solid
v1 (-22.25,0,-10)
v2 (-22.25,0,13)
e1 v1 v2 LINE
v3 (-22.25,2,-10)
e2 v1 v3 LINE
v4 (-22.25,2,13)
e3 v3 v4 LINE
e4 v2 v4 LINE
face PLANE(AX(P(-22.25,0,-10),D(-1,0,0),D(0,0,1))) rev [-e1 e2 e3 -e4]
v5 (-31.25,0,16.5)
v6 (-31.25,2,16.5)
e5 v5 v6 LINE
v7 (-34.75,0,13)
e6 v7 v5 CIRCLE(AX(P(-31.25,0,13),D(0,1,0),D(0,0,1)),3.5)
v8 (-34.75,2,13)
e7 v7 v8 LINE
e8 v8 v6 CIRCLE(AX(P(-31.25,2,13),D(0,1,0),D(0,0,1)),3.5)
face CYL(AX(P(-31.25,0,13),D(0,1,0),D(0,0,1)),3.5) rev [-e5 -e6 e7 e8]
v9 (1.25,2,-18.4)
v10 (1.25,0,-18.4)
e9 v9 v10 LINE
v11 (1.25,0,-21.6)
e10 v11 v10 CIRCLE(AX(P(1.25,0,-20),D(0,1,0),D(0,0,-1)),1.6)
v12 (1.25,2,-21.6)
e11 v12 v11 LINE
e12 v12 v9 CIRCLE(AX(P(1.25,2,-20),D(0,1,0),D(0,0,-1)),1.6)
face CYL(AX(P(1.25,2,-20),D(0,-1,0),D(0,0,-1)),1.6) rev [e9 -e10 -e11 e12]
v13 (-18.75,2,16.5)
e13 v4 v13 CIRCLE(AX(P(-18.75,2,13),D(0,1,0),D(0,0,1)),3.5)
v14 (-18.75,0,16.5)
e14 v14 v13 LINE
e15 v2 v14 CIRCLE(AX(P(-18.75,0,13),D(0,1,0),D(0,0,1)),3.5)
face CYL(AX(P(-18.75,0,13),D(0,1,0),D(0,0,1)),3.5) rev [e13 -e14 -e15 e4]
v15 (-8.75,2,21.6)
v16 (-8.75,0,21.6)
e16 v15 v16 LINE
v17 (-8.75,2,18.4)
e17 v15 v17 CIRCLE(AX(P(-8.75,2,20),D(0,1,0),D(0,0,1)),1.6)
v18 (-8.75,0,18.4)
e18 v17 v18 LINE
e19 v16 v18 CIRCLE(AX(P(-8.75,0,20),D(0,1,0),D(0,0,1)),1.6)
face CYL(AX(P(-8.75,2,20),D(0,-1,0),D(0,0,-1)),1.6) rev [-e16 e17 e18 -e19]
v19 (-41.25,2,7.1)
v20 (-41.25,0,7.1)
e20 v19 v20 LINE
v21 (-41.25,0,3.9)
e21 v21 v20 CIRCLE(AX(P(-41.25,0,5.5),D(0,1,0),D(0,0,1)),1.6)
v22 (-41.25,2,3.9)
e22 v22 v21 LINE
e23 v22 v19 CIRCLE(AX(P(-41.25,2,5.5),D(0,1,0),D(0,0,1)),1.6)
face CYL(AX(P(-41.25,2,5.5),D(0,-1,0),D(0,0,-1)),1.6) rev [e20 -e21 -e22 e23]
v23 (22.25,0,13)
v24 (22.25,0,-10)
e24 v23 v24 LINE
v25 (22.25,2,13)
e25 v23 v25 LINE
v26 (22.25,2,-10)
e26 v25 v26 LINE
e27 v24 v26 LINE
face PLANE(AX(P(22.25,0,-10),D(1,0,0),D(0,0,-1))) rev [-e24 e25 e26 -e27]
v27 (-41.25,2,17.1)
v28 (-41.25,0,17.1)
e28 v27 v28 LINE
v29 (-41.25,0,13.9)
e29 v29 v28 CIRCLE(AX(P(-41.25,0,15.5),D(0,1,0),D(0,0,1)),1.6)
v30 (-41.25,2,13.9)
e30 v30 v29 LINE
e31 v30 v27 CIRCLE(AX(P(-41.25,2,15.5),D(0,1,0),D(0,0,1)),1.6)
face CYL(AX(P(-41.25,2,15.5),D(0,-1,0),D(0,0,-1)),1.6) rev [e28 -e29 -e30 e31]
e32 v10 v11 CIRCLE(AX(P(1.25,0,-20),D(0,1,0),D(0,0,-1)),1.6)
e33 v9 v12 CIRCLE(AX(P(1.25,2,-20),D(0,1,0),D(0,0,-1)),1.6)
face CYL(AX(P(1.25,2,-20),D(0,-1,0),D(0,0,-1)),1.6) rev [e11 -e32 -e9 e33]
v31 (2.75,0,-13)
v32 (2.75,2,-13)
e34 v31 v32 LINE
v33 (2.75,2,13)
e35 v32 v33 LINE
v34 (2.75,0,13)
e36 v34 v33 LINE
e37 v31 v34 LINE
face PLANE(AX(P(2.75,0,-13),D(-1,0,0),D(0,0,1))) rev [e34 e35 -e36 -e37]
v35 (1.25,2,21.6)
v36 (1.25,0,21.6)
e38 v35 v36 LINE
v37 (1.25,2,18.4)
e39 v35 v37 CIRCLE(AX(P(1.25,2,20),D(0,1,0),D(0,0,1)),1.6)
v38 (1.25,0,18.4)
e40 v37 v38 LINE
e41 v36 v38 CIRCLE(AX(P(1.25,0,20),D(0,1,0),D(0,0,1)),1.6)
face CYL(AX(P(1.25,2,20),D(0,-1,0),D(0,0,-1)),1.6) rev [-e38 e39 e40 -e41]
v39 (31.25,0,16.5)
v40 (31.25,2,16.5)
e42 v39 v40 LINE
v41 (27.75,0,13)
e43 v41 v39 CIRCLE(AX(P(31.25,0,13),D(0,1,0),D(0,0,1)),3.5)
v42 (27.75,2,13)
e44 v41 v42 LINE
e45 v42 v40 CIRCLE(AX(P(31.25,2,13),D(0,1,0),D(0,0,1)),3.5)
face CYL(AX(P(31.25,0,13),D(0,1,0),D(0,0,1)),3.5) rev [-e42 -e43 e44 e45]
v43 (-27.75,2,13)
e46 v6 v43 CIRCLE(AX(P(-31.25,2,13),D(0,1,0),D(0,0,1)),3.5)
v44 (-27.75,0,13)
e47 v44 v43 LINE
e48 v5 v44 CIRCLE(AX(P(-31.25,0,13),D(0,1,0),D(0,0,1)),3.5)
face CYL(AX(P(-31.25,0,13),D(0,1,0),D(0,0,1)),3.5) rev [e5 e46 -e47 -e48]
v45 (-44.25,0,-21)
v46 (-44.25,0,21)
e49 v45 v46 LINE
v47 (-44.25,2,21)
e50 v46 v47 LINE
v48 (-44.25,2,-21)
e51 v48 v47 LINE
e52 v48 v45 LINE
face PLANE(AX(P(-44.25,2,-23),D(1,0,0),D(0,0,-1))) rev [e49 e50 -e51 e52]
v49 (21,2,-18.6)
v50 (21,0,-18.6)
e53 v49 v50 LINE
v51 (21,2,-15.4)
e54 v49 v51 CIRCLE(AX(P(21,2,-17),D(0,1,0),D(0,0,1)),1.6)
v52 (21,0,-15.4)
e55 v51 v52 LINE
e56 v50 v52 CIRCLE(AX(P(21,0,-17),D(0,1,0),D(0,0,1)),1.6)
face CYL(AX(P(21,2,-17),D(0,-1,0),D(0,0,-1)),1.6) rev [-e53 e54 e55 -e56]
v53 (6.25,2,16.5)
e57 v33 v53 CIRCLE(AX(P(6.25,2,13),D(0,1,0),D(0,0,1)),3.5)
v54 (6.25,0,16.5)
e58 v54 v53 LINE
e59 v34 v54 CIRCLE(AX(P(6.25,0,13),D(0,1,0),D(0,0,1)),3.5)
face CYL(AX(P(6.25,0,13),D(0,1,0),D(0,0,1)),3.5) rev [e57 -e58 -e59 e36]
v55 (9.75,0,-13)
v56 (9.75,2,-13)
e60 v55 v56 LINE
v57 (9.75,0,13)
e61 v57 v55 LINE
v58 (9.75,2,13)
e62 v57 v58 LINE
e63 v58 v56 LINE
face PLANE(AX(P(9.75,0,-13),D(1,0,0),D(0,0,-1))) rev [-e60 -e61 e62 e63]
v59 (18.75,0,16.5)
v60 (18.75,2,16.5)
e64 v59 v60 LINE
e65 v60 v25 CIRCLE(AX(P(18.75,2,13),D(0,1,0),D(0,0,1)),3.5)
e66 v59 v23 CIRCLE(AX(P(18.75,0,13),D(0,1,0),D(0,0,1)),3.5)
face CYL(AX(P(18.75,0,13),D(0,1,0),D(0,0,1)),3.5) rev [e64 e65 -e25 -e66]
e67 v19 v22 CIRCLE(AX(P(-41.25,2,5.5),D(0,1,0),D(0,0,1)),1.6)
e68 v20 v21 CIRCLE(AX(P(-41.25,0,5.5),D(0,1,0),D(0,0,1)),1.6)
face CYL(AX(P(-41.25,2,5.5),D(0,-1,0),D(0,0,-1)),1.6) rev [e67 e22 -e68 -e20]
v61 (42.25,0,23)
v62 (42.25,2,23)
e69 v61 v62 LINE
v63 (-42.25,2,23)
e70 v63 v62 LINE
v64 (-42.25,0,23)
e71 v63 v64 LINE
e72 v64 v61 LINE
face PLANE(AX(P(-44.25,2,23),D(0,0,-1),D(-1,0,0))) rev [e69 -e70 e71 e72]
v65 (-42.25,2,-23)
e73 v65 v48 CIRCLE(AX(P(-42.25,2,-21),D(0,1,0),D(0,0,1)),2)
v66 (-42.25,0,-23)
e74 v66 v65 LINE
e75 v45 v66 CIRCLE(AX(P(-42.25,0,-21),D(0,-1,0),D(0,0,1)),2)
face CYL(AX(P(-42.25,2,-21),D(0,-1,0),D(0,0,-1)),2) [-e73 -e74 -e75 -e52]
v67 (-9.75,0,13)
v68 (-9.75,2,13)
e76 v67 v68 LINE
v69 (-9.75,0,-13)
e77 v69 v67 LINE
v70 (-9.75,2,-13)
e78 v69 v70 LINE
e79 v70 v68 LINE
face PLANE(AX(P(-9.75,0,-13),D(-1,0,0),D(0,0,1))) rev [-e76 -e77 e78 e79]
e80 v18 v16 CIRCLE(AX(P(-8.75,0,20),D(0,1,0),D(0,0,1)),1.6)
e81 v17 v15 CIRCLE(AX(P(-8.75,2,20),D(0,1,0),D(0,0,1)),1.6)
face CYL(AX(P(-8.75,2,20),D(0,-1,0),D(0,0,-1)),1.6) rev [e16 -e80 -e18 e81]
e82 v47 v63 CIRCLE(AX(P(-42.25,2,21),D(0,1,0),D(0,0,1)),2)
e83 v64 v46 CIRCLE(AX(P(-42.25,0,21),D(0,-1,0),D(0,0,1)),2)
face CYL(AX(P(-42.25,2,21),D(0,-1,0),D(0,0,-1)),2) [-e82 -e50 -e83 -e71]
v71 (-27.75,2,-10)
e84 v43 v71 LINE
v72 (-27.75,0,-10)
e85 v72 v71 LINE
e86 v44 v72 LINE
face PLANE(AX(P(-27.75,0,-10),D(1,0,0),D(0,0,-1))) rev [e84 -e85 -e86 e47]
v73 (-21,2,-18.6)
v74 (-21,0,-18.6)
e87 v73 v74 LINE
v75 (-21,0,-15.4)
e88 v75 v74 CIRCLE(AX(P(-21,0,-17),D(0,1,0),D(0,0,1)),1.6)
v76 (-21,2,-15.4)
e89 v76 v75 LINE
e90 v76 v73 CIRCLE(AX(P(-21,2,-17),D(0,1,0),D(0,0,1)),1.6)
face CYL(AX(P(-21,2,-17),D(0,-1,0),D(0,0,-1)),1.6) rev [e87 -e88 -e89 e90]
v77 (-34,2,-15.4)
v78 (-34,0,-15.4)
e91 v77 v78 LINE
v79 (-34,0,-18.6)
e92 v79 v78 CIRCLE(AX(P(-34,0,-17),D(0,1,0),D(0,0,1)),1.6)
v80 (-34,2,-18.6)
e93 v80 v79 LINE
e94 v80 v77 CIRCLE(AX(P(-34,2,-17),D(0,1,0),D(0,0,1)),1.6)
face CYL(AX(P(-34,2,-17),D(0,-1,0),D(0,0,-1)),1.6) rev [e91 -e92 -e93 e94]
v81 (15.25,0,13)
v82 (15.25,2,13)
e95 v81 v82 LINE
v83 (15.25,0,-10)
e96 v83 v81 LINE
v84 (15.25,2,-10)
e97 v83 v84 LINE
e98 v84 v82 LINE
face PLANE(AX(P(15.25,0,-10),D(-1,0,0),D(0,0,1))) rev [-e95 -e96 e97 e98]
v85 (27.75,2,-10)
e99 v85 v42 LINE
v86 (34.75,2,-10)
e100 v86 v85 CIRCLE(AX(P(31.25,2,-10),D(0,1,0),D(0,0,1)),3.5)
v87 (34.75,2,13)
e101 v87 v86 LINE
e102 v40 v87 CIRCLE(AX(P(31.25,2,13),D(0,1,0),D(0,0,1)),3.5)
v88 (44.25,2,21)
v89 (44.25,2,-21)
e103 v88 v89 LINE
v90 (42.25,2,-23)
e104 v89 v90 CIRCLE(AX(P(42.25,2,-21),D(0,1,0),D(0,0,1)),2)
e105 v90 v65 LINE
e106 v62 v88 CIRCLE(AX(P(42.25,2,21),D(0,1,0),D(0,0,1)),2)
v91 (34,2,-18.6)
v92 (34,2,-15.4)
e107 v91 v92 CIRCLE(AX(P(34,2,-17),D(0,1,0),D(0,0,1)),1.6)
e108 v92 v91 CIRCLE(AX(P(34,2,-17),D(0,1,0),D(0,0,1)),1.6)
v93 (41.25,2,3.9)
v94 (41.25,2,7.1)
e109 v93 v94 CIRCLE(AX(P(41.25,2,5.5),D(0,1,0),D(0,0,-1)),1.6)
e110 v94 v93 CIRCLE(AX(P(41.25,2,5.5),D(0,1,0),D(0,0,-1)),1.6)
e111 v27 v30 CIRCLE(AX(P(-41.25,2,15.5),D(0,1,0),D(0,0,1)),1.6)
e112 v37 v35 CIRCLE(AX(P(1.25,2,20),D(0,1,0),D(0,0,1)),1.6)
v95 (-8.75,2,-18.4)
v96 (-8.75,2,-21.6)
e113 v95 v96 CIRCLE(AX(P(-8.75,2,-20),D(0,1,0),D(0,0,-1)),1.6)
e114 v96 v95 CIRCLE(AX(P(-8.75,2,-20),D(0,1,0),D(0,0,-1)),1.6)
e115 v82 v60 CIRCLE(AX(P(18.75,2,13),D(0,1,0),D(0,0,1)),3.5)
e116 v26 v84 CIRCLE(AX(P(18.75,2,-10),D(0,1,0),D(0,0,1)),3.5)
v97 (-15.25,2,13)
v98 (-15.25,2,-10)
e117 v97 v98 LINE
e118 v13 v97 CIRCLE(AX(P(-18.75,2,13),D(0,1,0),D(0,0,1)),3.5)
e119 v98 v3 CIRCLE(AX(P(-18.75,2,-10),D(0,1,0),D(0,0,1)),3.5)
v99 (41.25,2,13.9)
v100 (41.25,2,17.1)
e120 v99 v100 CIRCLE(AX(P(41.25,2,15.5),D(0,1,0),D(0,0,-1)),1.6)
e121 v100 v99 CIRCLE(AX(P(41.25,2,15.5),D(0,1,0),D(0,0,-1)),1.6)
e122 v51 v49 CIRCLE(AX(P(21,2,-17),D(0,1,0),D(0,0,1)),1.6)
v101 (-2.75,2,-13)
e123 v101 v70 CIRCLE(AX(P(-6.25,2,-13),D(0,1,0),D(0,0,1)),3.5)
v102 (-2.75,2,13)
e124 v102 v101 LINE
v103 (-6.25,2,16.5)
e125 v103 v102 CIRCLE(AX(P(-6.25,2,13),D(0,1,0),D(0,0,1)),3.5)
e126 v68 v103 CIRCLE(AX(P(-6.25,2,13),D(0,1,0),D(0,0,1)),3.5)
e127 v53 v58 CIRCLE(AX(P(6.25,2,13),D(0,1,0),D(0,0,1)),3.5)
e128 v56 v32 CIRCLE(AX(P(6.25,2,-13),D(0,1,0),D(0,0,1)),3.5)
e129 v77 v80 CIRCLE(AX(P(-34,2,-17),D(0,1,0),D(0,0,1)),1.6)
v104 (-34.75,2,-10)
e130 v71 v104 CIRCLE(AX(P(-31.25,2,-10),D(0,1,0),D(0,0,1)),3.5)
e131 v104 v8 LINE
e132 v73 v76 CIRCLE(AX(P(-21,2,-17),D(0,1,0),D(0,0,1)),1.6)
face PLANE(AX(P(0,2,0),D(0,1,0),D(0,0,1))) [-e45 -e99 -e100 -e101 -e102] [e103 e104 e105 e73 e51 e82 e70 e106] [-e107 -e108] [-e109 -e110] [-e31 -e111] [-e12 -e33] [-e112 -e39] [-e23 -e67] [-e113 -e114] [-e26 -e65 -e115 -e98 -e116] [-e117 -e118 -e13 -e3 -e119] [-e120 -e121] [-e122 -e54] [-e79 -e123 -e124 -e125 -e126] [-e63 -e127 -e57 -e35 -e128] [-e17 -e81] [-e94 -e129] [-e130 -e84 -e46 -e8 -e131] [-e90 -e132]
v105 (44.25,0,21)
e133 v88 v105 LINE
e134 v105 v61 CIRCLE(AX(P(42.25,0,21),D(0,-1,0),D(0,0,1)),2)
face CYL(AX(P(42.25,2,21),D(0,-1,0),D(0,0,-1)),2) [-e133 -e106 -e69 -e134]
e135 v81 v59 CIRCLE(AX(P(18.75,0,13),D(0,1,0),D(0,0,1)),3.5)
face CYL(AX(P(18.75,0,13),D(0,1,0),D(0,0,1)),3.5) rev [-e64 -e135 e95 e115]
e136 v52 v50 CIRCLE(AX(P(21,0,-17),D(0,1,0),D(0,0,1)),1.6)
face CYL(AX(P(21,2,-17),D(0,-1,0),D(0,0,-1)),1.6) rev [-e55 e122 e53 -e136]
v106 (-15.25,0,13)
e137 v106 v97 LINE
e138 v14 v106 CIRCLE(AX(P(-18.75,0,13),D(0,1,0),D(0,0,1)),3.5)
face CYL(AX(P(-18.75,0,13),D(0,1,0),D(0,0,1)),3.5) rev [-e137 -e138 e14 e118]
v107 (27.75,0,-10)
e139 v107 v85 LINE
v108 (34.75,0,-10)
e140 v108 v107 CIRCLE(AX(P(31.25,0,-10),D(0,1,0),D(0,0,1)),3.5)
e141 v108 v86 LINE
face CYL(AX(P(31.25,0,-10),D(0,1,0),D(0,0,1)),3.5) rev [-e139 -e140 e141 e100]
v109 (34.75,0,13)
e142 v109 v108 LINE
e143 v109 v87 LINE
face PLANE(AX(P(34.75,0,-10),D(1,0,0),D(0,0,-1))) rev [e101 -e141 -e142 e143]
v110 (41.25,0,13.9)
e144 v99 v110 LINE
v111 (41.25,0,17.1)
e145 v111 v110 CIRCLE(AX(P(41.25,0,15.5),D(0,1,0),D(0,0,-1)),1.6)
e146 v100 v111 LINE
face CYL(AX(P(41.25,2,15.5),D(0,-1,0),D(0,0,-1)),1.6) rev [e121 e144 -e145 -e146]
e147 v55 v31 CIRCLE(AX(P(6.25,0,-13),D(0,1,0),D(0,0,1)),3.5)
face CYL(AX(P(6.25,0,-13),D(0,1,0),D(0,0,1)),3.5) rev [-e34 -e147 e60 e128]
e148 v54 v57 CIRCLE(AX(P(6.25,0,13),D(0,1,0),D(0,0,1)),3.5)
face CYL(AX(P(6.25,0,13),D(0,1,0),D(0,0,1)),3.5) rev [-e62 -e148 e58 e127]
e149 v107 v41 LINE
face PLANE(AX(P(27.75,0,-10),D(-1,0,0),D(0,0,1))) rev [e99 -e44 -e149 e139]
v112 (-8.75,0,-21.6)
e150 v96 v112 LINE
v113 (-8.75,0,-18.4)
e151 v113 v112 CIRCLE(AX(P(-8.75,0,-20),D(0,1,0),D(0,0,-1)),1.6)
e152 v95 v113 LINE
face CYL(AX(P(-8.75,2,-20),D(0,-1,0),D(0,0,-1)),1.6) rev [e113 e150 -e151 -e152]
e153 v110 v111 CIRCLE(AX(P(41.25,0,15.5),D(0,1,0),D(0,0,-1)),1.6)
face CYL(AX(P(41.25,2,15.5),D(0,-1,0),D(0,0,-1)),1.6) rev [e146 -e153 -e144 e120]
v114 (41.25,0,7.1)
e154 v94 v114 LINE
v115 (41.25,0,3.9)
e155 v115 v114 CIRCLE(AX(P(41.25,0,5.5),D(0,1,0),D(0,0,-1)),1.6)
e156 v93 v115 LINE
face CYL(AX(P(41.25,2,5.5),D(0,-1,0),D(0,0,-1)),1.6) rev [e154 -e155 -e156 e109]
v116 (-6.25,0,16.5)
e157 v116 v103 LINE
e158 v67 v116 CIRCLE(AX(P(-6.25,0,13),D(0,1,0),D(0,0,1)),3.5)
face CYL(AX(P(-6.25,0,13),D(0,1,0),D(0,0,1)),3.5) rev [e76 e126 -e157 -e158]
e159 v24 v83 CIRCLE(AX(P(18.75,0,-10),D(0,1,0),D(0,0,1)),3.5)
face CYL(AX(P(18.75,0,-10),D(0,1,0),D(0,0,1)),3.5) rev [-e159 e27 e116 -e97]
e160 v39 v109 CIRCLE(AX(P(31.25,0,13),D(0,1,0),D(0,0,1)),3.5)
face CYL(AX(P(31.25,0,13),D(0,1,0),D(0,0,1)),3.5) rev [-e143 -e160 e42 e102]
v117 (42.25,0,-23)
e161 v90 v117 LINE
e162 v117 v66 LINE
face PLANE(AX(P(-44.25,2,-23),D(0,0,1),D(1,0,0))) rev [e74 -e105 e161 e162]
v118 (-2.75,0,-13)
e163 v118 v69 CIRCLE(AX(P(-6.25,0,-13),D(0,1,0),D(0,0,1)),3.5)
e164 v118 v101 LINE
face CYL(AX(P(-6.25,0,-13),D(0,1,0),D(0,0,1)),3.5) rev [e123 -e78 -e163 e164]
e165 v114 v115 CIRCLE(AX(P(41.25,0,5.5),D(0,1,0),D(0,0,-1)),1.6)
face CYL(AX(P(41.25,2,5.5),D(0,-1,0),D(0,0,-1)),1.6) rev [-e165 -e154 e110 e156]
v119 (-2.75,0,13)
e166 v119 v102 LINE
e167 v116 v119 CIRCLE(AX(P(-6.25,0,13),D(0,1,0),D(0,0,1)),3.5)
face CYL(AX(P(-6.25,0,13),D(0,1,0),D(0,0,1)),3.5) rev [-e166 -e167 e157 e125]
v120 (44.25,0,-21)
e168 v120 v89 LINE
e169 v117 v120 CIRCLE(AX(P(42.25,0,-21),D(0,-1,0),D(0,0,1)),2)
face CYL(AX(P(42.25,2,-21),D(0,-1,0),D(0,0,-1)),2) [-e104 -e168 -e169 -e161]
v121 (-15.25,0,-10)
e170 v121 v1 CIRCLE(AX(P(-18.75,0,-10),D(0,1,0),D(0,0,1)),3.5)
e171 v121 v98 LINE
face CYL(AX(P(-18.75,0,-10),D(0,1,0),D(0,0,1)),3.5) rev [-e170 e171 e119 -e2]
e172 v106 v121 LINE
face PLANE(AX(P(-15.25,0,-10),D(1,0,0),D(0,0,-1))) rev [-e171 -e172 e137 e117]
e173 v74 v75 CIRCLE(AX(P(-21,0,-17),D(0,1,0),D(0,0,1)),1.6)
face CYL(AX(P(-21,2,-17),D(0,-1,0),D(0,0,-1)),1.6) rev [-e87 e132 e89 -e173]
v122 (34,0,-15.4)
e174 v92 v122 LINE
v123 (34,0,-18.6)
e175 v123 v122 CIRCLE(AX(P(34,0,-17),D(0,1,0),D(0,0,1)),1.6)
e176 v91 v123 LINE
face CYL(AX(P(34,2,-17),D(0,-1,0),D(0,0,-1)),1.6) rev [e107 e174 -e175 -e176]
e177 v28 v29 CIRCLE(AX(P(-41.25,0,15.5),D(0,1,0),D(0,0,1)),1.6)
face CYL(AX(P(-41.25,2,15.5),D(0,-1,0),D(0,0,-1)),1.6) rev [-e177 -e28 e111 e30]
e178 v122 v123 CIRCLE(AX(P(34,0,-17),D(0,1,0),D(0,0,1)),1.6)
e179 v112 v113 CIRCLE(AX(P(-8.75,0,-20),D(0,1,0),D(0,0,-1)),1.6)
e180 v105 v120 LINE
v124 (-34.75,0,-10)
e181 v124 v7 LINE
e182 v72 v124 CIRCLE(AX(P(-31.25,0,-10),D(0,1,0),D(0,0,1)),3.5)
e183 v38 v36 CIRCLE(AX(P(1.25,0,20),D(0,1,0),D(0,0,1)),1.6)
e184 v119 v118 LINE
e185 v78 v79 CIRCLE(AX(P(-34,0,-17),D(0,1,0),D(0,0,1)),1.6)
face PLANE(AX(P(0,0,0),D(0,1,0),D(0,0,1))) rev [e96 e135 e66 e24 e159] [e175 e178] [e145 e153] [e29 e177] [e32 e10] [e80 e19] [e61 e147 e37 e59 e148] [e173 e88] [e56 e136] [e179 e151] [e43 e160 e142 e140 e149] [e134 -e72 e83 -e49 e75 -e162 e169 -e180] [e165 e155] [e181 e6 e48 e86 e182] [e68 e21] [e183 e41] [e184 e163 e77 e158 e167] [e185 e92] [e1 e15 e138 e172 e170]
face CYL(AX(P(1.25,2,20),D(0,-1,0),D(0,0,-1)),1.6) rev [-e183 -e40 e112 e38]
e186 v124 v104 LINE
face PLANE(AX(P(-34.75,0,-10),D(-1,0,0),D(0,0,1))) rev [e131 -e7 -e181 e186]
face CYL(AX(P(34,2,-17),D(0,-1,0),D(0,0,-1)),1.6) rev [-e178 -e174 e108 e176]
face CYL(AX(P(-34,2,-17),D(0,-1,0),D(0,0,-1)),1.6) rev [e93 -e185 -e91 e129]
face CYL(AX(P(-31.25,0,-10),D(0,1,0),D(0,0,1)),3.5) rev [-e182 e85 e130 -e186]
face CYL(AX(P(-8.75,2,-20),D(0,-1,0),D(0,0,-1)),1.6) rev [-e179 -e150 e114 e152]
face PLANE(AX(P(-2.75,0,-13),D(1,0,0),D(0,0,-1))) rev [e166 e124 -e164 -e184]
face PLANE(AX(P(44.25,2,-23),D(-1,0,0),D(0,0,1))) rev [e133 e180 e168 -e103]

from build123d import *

# Parameters (mm, degrees)
SKETCH_1_W          = 88.5
SKETCH_1_H          = 46
SKETCH_1_R          = 1.6
EXTRUDE_1_DEPTH     = 2
CUT_EXTRUDE_1_DEPTH = 50.910544978
FILLET_1_R          = 2


with BuildPart() as part:
    # 草图1 → 凸台-拉伸1 (new body)
    with BuildSketch(Plane(origin=(0, 0, 0), x_dir=(1, 0, 0), z_dir=(0, 1, 0))):
        Rectangle(SKETCH_1_W, SKETCH_1_H)
        with Locations(Location((-41.25, -5.5, 0), (0, 0, 270))):
            Circle(SKETCH_1_R, mode=Mode.SUBTRACT)
        with Locations(Location((-41.25, -15.5, 0), (0, 0, 270))):
            Circle(SKETCH_1_R, mode=Mode.SUBTRACT)
        with Locations(Location((41.25, -15.5, 0), (0, 0, 90))):
            Circle(SKETCH_1_R, mode=Mode.SUBTRACT)
        with Locations(Location((41.25, -5.5, 0), (0, 0, 90))):
            Circle(SKETCH_1_R, mode=Mode.SUBTRACT)
        with Locations(Location((-8.75, -20, 0), (0, 0, 270))):
            Circle(SKETCH_1_R, mode=Mode.SUBTRACT)
        with Locations(Location((1.25, -20, 0), (0, 0, 270))):
            Circle(SKETCH_1_R, mode=Mode.SUBTRACT)
        with Locations(Location((-34, 17, 0), (0, 0, 270))):
            Circle(SKETCH_1_R, mode=Mode.SUBTRACT)
        with Locations(Location((-21, 17, 0), (0, 0, 270))):
            Circle(SKETCH_1_R, mode=Mode.SUBTRACT)
        with Locations(Location((21, 17, 0), (0, 0, 270))):
            Circle(SKETCH_1_R, mode=Mode.SUBTRACT)
        with Locations(Location((34, 17, 0), (0, 0, 270))):
            Circle(SKETCH_1_R, mode=Mode.SUBTRACT)
        with Locations(Location((1.25, 20, 0), (0, 0, 90))):
            Circle(SKETCH_1_R, mode=Mode.SUBTRACT)
        with Locations(Location((-8.75, 20, 0), (0, 0, 90))):
            Circle(SKETCH_1_R, mode=Mode.SUBTRACT)
    extrude(amount=EXTRUDE_1_DEPTH)

    # 草图2 → 切除-拉伸1 (cut, through all)
    with BuildSketch(Plane(origin=(0, 2, 0), x_dir=(1, 0, 0), z_dir=(0, 1, 0))):
        with BuildLine():
            Line((-27.75, 10), (-27.75, -13))
            ThreePointArc((-27.75, -13), (-31.25, -16.5), (-34.75, -13))
            Line((-34.75, -13), (-34.75, 10))
            ThreePointArc((-34.75, 10), (-31.25, 13.5), (-27.75, 10))
        make_face()
        with BuildLine():
            Line((-15.25, 10), (-15.25, -13))
            ThreePointArc((-15.25, -13), (-18.75, -16.5), (-22.25, -13))
            Line((-22.25, -13), (-22.25, 10))
            ThreePointArc((-22.25, 10), (-18.75, 13.5), (-15.25, 10))
        make_face()
        with BuildLine():
            Line((-2.75, 13), (-2.75, -13))
            ThreePointArc((-2.75, -13), (-6.25, -16.5), (-9.75, -13))
            Line((-9.75, -13), (-9.75, 13))
            ThreePointArc((-9.75, 13), (-6.25, 16.5), (-2.75, 13))
        make_face()
        with BuildLine():
            Line((9.75, 13), (9.75, -13))
            ThreePointArc((9.75, -13), (6.25, -16.5), (2.75, -13))
            Line((2.75, -13), (2.75, 13))
            ThreePointArc((2.75, 13), (6.25, 16.5), (9.75, 13))
        make_face()
        with BuildLine():
            Line((22.25, 10), (22.25, -13))
            ThreePointArc((22.25, -13), (18.75, -16.5), (15.25, -13))
            Line((15.25, -13), (15.25, 10))
            ThreePointArc((15.25, 10), (18.75, 13.5), (22.25, 10))
        make_face()
        with BuildLine():
            Line((34.75, 10), (34.75, -13))
            ThreePointArc((34.75, -13), (31.25, -16.5), (27.75, -13))
            Line((27.75, -13), (27.75, 10))
            ThreePointArc((27.75, 10), (31.25, 13.5), (34.75, 10))
        make_face()
    extrude(amount=-CUT_EXTRUDE_1_DEPTH, mode=Mode.SUBTRACT)

    # 圆角1
    fillet_1_edges = [part.edges().sort_by_distance(p)[0] for p in [
        (44.25, 1, 23),
        (-44.25, 1, 23),
        (-44.25, 1, -23),
        (44.25, 1, -23),
    ]]
    fillet(fillet_1_edges, radius=FILLET_1_R)


solid = part.part
